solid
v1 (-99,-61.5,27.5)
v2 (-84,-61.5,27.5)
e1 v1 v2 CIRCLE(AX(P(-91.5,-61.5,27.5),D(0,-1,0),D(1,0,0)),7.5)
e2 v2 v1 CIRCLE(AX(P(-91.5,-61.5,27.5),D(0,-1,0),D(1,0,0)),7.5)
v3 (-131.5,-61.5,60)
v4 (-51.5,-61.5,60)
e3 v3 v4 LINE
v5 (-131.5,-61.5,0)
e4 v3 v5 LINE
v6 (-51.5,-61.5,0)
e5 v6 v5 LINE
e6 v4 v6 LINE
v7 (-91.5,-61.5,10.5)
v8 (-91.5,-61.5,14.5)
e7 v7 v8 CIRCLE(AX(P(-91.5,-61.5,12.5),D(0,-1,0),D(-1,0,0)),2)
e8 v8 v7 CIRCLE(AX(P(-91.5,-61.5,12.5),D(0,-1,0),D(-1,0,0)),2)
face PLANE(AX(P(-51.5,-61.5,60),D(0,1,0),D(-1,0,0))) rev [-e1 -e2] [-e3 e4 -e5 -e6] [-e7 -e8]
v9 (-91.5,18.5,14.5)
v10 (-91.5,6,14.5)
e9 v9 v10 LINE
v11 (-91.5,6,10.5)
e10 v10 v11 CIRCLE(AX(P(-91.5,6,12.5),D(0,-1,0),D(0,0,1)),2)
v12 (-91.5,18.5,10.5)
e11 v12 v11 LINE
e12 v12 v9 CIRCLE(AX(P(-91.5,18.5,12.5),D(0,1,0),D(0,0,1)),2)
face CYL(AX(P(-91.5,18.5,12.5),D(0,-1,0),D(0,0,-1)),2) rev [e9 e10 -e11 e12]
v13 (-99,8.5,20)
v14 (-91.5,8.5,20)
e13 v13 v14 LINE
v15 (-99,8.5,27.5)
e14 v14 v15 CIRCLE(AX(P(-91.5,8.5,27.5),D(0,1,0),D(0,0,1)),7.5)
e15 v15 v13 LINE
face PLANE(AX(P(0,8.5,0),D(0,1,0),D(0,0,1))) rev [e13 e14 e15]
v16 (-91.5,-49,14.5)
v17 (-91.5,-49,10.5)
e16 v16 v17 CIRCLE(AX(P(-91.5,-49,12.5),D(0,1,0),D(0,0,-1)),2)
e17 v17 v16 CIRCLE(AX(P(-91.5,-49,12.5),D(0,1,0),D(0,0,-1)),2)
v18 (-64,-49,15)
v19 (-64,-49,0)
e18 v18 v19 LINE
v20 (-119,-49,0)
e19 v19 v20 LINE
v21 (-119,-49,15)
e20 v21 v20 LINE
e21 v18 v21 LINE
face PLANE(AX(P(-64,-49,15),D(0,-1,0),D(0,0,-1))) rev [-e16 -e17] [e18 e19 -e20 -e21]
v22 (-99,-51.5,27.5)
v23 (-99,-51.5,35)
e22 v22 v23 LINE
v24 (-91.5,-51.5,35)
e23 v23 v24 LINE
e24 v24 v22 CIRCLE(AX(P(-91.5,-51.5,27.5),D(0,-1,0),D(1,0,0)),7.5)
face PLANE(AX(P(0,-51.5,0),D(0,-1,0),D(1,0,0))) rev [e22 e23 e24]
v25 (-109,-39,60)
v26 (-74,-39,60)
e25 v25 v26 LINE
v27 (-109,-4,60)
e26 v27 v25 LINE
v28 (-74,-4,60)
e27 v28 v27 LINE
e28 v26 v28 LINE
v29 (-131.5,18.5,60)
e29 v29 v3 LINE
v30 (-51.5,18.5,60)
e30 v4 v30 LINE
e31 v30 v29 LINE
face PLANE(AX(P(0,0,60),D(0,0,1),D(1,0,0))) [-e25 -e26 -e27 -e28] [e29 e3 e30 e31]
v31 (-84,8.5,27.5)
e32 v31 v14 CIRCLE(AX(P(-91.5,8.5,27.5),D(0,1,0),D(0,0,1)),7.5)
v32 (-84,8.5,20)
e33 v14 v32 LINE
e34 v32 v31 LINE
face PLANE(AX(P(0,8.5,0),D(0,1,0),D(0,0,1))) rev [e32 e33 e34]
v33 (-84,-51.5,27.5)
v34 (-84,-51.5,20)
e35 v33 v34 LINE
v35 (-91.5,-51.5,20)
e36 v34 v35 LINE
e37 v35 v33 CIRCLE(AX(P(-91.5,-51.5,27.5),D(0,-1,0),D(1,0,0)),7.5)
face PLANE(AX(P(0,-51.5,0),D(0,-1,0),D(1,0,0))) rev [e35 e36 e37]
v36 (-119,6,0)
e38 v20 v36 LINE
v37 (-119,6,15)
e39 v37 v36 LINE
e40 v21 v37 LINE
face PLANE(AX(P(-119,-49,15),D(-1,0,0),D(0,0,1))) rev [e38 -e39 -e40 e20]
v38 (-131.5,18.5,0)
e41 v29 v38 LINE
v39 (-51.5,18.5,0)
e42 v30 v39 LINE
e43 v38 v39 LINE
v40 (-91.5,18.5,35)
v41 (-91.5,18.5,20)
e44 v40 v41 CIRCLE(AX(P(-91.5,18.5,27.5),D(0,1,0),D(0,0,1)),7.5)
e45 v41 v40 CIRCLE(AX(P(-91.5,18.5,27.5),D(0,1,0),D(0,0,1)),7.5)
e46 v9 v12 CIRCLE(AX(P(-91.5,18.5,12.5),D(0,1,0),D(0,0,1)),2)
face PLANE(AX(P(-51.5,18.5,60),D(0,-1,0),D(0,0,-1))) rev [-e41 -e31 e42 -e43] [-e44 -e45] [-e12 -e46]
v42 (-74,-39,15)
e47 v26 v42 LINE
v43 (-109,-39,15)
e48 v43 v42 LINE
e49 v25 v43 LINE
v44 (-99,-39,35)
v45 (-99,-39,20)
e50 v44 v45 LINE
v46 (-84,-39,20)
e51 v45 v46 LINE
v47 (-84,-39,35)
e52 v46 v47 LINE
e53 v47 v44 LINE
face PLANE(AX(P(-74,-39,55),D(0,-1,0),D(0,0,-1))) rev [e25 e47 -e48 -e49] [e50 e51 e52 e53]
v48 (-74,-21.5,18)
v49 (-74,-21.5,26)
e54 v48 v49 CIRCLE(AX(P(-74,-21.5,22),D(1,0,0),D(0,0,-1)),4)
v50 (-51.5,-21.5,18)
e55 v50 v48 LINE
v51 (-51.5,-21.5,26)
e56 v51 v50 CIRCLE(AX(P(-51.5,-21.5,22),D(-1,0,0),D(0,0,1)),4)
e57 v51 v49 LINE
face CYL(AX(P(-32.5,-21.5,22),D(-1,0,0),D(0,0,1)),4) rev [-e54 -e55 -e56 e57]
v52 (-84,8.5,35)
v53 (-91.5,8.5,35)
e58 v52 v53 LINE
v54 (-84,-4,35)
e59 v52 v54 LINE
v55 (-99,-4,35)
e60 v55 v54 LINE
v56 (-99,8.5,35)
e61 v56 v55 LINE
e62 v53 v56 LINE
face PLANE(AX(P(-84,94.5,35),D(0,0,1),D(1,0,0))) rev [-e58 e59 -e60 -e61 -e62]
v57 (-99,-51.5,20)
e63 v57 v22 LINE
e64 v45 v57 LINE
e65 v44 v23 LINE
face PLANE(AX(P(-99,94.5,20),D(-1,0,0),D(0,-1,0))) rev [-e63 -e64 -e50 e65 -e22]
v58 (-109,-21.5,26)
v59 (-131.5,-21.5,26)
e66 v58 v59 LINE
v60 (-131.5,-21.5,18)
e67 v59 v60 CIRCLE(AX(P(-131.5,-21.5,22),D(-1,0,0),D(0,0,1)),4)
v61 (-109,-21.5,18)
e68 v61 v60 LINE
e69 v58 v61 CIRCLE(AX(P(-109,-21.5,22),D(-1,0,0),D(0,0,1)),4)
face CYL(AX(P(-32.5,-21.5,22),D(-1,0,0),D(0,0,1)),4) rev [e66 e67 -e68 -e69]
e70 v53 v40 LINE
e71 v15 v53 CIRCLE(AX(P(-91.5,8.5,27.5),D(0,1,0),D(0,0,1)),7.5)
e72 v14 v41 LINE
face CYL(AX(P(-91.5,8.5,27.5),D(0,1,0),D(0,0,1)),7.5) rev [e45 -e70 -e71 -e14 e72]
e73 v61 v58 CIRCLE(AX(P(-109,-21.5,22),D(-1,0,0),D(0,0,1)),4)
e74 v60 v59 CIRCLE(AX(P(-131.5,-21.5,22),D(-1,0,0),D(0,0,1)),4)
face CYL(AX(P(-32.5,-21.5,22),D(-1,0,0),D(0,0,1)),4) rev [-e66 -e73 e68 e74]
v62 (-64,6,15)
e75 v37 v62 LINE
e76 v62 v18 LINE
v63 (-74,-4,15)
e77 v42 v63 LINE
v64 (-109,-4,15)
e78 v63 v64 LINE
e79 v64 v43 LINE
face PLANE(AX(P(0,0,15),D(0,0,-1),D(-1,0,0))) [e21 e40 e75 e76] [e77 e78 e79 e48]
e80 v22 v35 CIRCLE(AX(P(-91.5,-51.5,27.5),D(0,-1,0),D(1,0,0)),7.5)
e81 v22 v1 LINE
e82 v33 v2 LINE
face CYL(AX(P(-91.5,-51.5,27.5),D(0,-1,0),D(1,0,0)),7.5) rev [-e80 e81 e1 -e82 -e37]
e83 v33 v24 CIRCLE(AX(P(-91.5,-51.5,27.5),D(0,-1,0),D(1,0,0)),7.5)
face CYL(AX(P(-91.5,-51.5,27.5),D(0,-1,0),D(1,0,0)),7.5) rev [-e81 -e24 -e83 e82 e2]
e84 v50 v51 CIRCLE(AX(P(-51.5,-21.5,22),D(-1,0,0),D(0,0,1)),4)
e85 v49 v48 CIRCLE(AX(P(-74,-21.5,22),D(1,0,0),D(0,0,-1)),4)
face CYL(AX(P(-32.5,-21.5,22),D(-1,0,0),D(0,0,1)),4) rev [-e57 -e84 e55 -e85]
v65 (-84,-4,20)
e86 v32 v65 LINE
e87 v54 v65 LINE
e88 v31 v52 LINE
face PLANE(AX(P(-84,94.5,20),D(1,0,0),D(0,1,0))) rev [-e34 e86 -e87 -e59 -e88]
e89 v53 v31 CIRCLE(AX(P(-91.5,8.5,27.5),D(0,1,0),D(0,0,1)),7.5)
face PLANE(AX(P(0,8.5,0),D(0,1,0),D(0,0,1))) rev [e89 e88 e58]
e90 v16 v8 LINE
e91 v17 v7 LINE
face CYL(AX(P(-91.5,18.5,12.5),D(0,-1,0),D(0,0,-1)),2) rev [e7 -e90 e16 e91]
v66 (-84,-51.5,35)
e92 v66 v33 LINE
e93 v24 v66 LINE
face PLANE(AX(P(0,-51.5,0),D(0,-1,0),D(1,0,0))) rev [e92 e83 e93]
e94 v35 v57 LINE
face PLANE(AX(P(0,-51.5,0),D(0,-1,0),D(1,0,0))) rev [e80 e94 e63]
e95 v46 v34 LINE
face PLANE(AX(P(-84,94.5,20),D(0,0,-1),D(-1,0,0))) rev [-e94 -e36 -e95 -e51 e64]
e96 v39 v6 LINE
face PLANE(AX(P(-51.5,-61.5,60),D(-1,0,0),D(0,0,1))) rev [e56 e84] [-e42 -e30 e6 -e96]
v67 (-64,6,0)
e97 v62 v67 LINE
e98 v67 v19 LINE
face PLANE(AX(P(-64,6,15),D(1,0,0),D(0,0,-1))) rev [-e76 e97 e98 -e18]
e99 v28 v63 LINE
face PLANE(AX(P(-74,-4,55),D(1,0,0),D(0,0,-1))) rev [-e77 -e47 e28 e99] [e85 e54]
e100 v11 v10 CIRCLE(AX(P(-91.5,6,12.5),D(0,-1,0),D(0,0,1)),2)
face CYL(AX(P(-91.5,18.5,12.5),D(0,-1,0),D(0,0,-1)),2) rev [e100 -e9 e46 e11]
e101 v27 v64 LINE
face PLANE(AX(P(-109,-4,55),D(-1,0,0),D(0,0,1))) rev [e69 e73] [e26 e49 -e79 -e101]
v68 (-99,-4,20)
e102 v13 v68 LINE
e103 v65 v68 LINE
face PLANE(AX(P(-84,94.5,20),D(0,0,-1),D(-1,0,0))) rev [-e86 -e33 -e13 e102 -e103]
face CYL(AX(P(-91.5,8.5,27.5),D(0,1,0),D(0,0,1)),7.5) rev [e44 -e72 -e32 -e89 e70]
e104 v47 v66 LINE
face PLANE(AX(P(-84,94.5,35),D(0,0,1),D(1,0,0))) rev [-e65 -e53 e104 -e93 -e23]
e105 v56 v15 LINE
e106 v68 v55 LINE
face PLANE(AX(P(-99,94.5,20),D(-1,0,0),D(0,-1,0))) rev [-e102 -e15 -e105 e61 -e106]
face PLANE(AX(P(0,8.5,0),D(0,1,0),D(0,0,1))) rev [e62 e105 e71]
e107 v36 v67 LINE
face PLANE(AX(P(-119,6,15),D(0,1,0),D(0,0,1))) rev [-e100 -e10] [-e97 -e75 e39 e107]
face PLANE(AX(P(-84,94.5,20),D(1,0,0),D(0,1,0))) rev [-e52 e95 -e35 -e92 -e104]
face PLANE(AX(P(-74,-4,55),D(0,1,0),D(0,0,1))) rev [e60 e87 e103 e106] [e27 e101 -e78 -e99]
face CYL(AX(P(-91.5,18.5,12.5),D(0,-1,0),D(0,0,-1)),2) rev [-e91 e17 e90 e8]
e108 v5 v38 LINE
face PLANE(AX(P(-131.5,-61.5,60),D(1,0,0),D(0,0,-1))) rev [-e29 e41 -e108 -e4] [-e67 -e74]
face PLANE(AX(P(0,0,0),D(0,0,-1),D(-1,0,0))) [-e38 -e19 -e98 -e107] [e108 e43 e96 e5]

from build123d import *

# Parameters (mm, degrees)
BOSS_EXTRUDE1_START     = 10
SKETCH1_W               = 80
SKETCH1_H               = 80
BOSS_EXTRUDE1_DEPTH     = 50
SKETCH2_W               = 35
SKETCH2_H               = 35
CUT_EXTRUDE1_DEPTH      = 45
SKETCH3_W               = 55
SKETCH3_H               = 55
CUT_EXTRUDE2_DEPTH      = 5
SKETCH4_W               = 15
SKETCH4_H               = 15
CUT_EXTRUDE3_DEPTH      = 156
BOSS_EXTRUDE2_DEPTH     = 10
BOSS_EXTRUDE3_START     = -10
BOSS_EXTRUDE3_DEPTH     = 10
SKETCH9_R               = 4
CUT_EXTRUDE6_DEPTH      = 99
SKETCH13_W              = 35
SKETCH13_H              = 35
CUT_EXTRUDE7_DEPTH      = 200
CUT_EXTRUDE8_DEPTH      = 160.525859973
CUT_EXTRUDE8_DEPTH_BACK = 43
SKETCH14_R              = 2
SKETCH15_W              = 80
SKETCH15_H              = 80
SKETCH15_W_2            = 55
SKETCH15_H_2            = 55
BOSS_EXTRUDE4_DEPTH     = 10


with BuildPart() as part:
    # Sketch1 → Boss-Extrude1 (new body)
    with BuildSketch(Plane.XY.offset(BOSS_EXTRUDE1_START)):
        with Locations((-91.5, -21.5)):
            Rectangle(SKETCH1_W, SKETCH1_H)
    extrude(amount=BOSS_EXTRUDE1_DEPTH)

    # Sketch2 → Cut-Extrude1 (cut)
    with BuildSketch(Plane(origin=(0, 0, 10), x_dir=(-1, 0, 0), z_dir=(0, 0, -1))):
        with Locations((91.5, -21.5)):
            Rectangle(SKETCH2_W, SKETCH2_H)
    extrude(amount=-CUT_EXTRUDE1_DEPTH, mode=Mode.SUBTRACT)

    # Sketch3 → Cut-Extrude2 (cut)
    with BuildSketch(Plane(origin=(0, 0, 10), x_dir=(-1, 0, 0), z_dir=(0, 0, -1))):
        with Locations((91.5, -21.5)):
            Rectangle(SKETCH3_W, SKETCH3_H)
    extrude(amount=-CUT_EXTRUDE2_DEPTH, mode=Mode.SUBTRACT)

    # Sketch4 → Cut-Extrude3 (cut)
    with BuildSketch(Plane(origin=(0, -61.5, 0), x_dir=(-1, 0, 0), z_dir=(0, -1, 0))):
        with Locations((91.5, -27.5)):
            Rectangle(SKETCH4_W, SKETCH4_H)
    extrude(amount=-CUT_EXTRUDE3_DEPTH, mode=Mode.SUBTRACT)

    # Sketch5 → Boss-Extrude2 (add)
    with BuildSketch(Plane.XZ.offset(61.5)):
        with BuildLine():
            Line((-99, 27.5), (-99, 20))
            Line((-99, 20), (-91.499999963, 20))
            ThreePointArc((-91.499999963, 20), (-96.803300846, 22.196699128), (-99, 27.5))
        make_face()
        with BuildLine():
            ThreePointArc((-84, 27.5), (-86.196699128, 22.196699154), (-91.499999963, 20))
            Line((-91.499999963, 20), (-84, 20))
            Line((-84, 20), (-84, 27.5))
        make_face()
        with BuildLine():
            ThreePointArc((-91.5, 35), (-86.196699141, 32.803300859), (-84, 27.5))
            Line((-84, 27.5), (-84, 35))
            Line((-84, 35), (-91.5, 35))
        make_face()
        with BuildLine():
            Line((-99, 35), (-99, 27.5))
            ThreePointArc((-99, 27.5), (-96.803300859, 32.803300859), (-91.5, 35))
            Line((-91.5, 35), (-99, 35))
        make_face()
    extrude(amount=-BOSS_EXTRUDE2_DEPTH)

    # Sketch6 → Boss-Extrude3 (add)
    with BuildSketch(Plane(origin=(0, 18.5, 0), x_dir=(1, 0, 0), z_dir=(0, 1, 0)).offset(BOSS_EXTRUDE3_START)):
        with BuildLine():
            Line((-84, -27.5), (-84, -20))
            Line((-84, -20), (-91.5, -20))
            ThreePointArc((-91.5, -20), (-86.196699141, -22.196699141), (-84, -27.5))
        make_face()
        with BuildLine():
            ThreePointArc((-99, -27.5), (-96.803300859, -22.196699141), (-91.5, -20))
            Line((-91.5, -20), (-99, -20))
            Line((-99, -20), (-99, -27.5))
        make_face()
        with BuildLine():
            ThreePointArc((-91.5, -35), (-96.803300859, -32.803300859), (-99, -27.5))
            Line((-99, -27.5), (-99, -35))
            Line((-99, -35), (-91.5, -35))
        make_face()
        with BuildLine():
            Line((-84, -35), (-84, -27.5))
            ThreePointArc((-84, -27.5), (-86.196699141, -32.803300859), (-91.5, -35))
            Line((-91.5, -35), (-84, -35))
        make_face()
    extrude(amount=BOSS_EXTRUDE3_DEPTH)

    # Sketch9 → Cut-Extrude6 (cut)
    with BuildSketch(Plane.ZY.offset(131.5)):
        with Locations((22, -21.5)):
            Circle(SKETCH9_R)
    extrude(amount=-CUT_EXTRUDE6_DEPTH, mode=Mode.SUBTRACT)

    # Sketch13 → Cut-Extrude7 (cut)
    with BuildSketch(Plane(origin=(0, 0, 55), x_dir=(-1, 0, 0), z_dir=(0, 0, -1))):
        with Locations((91.5, -21.5)):
            Rectangle(SKETCH13_W, SKETCH13_H)
    extrude(amount=-CUT_EXTRUDE7_DEPTH, mode=Mode.SUBTRACT)

    # Sketch14 → Cut-Extrude8 (cut, two sides: drawn at the far end of the back side and taken through both)
    with BuildSketch(Plane(origin=(0, -49, 0), x_dir=(1, 0, 0), z_dir=(0, 1, 0)).offset(-CUT_EXTRUDE8_DEPTH_BACK)):
        with Locations(Location((-91.5, -12.5, 0), (0, 0, 270))):
            Circle(SKETCH14_R)
    extrude(amount=CUT_EXTRUDE8_DEPTH + CUT_EXTRUDE8_DEPTH_BACK, mode=Mode.SUBTRACT)

    # Sketch15 → Boss-Extrude4 (add)
    with BuildSketch(Plane(origin=(0, 0, 10), x_dir=(-1, 0, 0), z_dir=(0, 0, -1))):
        with Locations((91.5, -21.5)):
            Rectangle(SKETCH15_W, SKETCH15_H)
        with Locations((91.5, -21.5)):
            Rectangle(SKETCH15_W_2, SKETCH15_H_2, mode=Mode.SUBTRACT)
    extrude(amount=BOSS_EXTRUDE4_DEPTH)


solid = part.part
